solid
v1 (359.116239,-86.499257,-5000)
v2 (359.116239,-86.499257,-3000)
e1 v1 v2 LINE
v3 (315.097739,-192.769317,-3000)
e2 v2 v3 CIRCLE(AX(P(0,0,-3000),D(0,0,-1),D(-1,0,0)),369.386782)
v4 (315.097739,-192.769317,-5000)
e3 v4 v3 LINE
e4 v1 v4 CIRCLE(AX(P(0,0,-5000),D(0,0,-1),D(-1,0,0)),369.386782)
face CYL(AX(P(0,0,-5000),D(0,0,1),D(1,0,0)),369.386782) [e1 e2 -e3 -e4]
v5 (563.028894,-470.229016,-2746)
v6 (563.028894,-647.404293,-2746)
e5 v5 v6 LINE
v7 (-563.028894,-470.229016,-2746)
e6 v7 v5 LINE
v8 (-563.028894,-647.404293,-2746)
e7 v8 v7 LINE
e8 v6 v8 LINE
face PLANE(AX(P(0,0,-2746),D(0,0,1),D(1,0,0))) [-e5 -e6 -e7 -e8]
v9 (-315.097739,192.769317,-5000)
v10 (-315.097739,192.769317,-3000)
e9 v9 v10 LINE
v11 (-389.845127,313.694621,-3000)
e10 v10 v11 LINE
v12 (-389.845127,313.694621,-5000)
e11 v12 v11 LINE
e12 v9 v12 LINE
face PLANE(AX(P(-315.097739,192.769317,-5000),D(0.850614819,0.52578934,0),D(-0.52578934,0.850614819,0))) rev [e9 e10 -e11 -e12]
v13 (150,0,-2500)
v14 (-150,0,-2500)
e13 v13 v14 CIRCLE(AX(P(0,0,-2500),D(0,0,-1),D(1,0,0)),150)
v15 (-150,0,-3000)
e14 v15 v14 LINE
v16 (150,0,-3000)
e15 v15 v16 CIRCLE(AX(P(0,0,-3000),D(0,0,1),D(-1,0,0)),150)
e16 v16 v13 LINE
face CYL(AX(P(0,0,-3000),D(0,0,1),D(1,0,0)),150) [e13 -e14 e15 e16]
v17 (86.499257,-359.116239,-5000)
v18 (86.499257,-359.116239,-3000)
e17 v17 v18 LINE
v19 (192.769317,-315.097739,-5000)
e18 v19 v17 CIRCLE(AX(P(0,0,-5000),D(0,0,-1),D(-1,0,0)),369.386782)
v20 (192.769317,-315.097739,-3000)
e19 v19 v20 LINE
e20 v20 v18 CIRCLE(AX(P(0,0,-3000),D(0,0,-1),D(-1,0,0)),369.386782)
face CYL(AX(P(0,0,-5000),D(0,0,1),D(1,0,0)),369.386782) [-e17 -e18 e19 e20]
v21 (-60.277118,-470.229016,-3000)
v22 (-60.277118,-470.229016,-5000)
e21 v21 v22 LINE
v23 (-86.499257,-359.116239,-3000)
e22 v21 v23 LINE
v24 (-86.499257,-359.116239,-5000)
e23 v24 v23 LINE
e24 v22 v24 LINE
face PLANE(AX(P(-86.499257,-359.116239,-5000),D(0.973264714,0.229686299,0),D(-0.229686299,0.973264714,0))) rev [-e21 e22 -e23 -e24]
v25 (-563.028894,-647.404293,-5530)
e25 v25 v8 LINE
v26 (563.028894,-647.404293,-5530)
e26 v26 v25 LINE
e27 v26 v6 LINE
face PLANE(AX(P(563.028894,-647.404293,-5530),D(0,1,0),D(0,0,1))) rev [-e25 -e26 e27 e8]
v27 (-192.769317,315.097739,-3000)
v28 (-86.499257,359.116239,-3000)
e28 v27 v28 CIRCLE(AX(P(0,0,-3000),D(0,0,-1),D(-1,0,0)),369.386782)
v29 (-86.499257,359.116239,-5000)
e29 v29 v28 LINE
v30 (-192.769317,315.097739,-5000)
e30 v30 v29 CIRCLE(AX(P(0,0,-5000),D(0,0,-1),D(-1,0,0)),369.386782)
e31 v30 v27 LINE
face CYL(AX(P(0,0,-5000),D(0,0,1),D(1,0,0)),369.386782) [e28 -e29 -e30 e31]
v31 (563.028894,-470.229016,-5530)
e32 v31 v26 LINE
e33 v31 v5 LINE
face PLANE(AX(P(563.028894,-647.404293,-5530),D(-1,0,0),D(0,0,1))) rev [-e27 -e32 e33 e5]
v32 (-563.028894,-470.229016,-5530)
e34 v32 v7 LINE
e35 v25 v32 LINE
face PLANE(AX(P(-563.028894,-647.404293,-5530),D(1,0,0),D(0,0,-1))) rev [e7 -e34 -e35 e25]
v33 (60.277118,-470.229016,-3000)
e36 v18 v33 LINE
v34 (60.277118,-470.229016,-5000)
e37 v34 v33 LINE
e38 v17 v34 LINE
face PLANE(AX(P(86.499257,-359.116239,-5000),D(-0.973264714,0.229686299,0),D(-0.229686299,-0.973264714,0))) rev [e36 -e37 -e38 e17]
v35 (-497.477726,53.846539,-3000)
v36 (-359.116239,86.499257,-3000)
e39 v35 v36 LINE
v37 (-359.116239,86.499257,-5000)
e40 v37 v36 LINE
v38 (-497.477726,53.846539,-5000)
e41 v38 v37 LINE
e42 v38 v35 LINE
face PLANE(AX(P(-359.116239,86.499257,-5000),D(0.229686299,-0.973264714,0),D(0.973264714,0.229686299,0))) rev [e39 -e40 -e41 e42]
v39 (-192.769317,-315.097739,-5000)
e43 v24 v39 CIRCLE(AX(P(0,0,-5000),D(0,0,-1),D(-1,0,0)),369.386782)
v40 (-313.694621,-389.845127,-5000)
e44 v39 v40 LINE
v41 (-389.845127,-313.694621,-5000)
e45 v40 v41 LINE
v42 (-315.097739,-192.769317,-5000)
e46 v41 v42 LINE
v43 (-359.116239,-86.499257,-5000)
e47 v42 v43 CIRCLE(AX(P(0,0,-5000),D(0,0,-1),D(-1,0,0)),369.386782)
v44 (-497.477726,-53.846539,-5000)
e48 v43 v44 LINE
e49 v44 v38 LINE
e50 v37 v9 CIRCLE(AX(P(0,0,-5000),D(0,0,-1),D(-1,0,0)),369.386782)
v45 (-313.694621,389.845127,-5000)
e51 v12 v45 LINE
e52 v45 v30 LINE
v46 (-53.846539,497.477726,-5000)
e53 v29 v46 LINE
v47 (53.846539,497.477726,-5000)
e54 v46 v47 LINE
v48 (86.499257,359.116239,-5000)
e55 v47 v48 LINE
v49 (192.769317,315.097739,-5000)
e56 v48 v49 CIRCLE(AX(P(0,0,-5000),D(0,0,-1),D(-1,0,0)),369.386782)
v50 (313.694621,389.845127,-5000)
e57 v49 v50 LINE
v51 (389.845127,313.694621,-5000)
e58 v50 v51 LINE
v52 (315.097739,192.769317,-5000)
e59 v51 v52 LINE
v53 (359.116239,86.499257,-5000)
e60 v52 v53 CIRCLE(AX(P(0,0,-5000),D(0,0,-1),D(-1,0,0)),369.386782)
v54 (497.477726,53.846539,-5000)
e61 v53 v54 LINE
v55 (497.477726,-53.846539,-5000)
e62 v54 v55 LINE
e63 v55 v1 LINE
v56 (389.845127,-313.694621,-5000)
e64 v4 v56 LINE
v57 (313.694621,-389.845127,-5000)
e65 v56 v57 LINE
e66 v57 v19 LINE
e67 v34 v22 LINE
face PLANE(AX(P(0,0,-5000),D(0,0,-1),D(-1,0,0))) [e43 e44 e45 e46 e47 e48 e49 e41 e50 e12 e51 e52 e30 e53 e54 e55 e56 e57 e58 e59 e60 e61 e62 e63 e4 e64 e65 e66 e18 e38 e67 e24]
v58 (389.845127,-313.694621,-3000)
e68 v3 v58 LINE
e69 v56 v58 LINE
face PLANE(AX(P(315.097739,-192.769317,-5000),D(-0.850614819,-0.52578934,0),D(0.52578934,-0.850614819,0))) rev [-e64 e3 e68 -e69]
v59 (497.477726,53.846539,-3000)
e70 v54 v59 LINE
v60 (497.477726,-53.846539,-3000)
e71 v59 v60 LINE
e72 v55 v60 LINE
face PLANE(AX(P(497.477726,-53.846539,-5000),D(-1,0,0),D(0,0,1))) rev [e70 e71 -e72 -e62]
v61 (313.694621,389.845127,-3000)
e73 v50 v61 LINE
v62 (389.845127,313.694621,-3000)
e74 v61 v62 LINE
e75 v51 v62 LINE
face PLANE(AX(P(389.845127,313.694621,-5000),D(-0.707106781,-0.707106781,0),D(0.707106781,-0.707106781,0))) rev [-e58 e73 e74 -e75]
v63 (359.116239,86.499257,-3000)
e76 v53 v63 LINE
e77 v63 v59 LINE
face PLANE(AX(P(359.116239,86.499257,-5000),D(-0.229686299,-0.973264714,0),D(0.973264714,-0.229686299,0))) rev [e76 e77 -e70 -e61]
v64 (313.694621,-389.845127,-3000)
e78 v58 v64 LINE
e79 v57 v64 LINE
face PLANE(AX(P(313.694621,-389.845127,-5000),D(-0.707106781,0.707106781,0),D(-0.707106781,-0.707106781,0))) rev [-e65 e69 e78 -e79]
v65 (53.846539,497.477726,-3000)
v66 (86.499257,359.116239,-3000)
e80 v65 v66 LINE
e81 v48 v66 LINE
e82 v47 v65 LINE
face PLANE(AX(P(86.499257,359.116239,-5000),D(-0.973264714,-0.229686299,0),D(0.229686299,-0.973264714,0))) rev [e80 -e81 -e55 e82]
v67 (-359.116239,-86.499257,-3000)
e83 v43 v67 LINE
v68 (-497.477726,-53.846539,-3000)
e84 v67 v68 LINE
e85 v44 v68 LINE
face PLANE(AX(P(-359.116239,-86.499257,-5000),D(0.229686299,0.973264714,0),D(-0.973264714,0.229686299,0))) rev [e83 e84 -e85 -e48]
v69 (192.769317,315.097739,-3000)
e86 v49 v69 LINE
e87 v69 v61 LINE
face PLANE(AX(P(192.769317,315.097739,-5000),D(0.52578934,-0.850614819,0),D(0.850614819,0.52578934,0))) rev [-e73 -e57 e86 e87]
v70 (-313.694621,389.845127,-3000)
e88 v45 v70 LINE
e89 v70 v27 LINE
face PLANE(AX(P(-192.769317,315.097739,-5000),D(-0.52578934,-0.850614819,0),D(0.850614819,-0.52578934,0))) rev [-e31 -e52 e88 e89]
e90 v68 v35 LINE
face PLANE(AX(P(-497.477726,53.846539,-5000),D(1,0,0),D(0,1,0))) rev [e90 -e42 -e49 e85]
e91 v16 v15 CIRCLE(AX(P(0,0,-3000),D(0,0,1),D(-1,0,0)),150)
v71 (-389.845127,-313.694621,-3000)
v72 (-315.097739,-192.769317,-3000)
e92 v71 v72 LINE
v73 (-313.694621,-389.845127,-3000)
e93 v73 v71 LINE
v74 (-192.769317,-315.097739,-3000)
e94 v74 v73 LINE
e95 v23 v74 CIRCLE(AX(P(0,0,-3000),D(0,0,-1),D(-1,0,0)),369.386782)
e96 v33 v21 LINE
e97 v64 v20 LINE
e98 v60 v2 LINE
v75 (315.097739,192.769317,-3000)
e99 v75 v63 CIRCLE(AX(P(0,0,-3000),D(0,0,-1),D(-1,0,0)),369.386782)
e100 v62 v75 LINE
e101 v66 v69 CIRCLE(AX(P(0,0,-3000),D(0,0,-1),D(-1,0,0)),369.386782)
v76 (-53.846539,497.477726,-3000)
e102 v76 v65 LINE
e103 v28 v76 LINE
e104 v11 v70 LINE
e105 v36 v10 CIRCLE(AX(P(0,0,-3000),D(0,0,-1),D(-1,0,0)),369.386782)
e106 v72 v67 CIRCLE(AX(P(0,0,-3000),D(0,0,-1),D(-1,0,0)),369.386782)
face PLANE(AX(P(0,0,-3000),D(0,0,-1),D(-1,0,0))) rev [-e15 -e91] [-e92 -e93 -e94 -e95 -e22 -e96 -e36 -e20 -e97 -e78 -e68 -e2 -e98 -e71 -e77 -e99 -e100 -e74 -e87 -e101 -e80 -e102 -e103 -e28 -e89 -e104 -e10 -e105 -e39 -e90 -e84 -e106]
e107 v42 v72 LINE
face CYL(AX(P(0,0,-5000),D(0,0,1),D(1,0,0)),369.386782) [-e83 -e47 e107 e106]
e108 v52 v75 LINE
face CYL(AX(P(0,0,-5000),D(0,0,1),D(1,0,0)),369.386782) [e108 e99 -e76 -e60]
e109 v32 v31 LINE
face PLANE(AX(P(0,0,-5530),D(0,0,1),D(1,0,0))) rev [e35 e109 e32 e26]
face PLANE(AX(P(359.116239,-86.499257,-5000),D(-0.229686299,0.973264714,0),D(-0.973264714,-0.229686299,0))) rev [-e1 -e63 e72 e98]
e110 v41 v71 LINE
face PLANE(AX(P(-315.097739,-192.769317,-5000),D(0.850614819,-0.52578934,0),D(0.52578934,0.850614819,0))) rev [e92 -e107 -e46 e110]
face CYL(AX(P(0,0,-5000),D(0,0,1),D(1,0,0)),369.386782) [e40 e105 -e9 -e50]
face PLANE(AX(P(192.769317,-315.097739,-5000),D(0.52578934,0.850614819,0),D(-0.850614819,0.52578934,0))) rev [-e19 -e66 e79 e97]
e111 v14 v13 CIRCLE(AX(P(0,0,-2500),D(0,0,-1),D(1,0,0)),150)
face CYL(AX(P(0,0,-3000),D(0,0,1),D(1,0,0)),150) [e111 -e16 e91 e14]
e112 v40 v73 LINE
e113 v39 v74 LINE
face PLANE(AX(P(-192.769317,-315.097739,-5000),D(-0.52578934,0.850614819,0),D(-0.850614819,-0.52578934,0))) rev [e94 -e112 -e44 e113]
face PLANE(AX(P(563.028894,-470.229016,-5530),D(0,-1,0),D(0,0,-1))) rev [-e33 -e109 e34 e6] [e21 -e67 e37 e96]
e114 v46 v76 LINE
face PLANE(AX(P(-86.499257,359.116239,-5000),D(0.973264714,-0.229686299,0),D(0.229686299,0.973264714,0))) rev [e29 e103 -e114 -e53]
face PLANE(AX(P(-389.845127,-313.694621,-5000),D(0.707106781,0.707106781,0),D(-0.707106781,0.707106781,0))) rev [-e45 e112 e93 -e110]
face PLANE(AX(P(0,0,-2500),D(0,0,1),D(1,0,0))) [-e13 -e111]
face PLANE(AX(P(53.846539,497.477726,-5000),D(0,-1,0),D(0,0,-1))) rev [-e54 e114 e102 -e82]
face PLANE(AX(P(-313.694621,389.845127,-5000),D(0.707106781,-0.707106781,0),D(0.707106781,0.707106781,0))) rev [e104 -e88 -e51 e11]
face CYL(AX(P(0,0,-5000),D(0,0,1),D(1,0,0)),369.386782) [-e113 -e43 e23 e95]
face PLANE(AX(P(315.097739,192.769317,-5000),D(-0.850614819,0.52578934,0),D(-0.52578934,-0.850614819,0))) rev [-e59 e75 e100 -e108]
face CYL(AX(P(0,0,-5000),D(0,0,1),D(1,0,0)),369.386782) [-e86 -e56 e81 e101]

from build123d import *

# Parameters (mm, degrees)
SKETCH1_R                = 150
BOSS_EXTRUDE1_DEPTH      = 3000
CUT_EXTRUDE1_DEPTH       = 435
BOSS_EXTRUDE3_DEPTH      = 2000
BOSS_EXTRUDE4_DEPTH      = 530
BOSS_EXTRUDE4_DEPTH_BACK = 2254
SKETCH5_W                = 1126.0577882
SKETCH5_H                = 177.175277377
BOSS_EXTRUDE5_DEPTH      = 75
SKETCH8_R                = 377.253593713
CUT_EXTRUDE2_DEPTH       = 2500


with BuildPart() as part:
    # Sketch1 → Boss-Extrude1 (new body)
    with BuildSketch(Plane.XY):
        Circle(SKETCH1_R)
    extrude(amount=-BOSS_EXTRUDE1_DEPTH)

    # Sketch2 → Cut-Extrude1 (cut)
    with BuildSketch(Plane(origin=(0, 0, 0), x_dir=(1, 0, 0), z_dir=(0, 1, 0))):
        with BuildLine():
            Line((-50, 150), (-50, 450))
            ThreePointArc((-50, 450), (0, 500), (50, 450))
            Line((50, 450), (50, 150))
            ThreePointArc((50, 150), (0, 100), (-50, 150))
        make_face()
    extrude(amount=CUT_EXTRUDE1_DEPTH, mode=Mode.SUBTRACT)

    # Sketch4 → Boss-Extrude3 (add)
    with BuildSketch(Plane(origin=(0, 0, -3000), x_dir=(-1, 0, 0), z_dir=(0, 0, -1))):
        with BuildLine():
            Line((-86.499256684, 359.11623894), (-53.846539015, 497.477726118))
            Line((-53.846539015, 497.477726118), (53.846539015, 497.477726118))
            Line((53.846539015, 497.477726118), (86.499256684, 359.11623894))
            ThreePointArc((86.499256684, 359.11623894), (141.358201482, 341.268887171), (192.76931682, 315.097738757))
            Line((192.76931682, 315.097738757), (313.694620747, 389.845126508))
            Line((313.694620747, 389.845126508), (389.845126508, 313.694620747))
            Line((389.845126508, 313.694620747), (315.097738757, 192.76931682))
            ThreePointArc((315.097738757, 192.76931682), (341.268887171, 141.358201482), (359.11623894, 86.499256684))
            Line((359.11623894, 86.499256684), (497.477726118, 53.846539015))
            Line((497.477726118, 53.846539015), (497.477726118, -53.846539015))
            Line((497.477726118, -53.846539015), (359.11623894, -86.499256684))
            ThreePointArc((359.11623894, -86.499256684), (341.268887171, -141.358201482), (315.097738757, -192.76931682))
            Line((315.097738757, -192.76931682), (389.845126508, -313.694620747))
            Line((389.845126508, -313.694620747), (313.694620747, -389.845126508))
            Line((313.694620747, -389.845126508), (192.76931682, -315.097738757))
            ThreePointArc((192.76931682, -315.097738757), (141.358201482, -341.268887171), (86.499256684, -359.11623894))
            Line((86.499256684, -359.11623894), (53.846539015, -497.477726118))
            Line((53.846539015, -497.477726118), (-53.846539015, -497.477726118))
            Line((-53.846539015, -497.477726118), (-86.499256684, -359.11623894))
            ThreePointArc((-86.499256684, -359.11623894), (-141.358201482, -341.268887171), (-192.76931682, -315.097738757))
            Line((-192.76931682, -315.097738757), (-313.694620747, -389.845126508))
            Line((-313.694620747, -389.845126508), (-389.845126508, -313.694620747))
            Line((-389.845126508, -313.694620747), (-315.097738757, -192.76931682))
            ThreePointArc((-315.097738757, -192.76931682), (-341.268887171, -141.358201482), (-359.11623894, -86.499256684))
            Line((-359.11623894, -86.499256684), (-497.477726118, -53.846539015))
            Line((-497.477726118, -53.846539015), (-497.477726118, 53.846539015))
            Line((-497.477726118, 53.846539015), (-359.11623894, 86.499256684))
            ThreePointArc((-359.11623894, 86.499256684), (-341.268887171, 141.358201482), (-315.097738757, 192.76931682))
            Line((-315.097738757, 192.76931682), (-389.845126508, 313.694620747))
            Line((-389.845126508, 313.694620747), (-313.694620747, 389.845126508))
            Line((-313.694620747, 389.845126508), (-192.76931682, 315.097738757))
            ThreePointArc((-192.76931682, 315.097738757), (-141.358201482, 341.268887171), (-86.499256684, 359.11623894))
        make_face()
    extrude(amount=BOSS_EXTRUDE3_DEPTH)

    # Sketch5 → Boss-Extrude4 (add, two sides: drawn at the far end of the back side and taken through both)
    with BuildSketch(Plane(origin=(0, 0, -5000), x_dir=(-1, 0, 0), z_dir=(0, 0, -1)).offset(-BOSS_EXTRUDE4_DEPTH_BACK)):
        with Locations((0, -558.816654709)):
            Rectangle(SKETCH5_W, SKETCH5_H)
    extrude(amount=BOSS_EXTRUDE4_DEPTH + BOSS_EXTRUDE4_DEPTH_BACK)

    # Sketch6 → Boss-Extrude5 (add)
    with BuildSketch(Plane(origin=(0, 0, 0), x_dir=(1, 0, 0), z_dir=(0, 1, 0))):
        with BuildLine():
            Line((50, 150), (50, 450))
            ThreePointArc((50, 450), (0, 500), (-50, 450))
            Line((-50, 450), (-50, 150))
            ThreePointArc((-50, 150), (0, 100), (50, 150))
        make_face()
    extrude(amount=BOSS_EXTRUDE5_DEPTH)

    # Sketch8 → Cut-Extrude2 (cut)
    with BuildSketch(Plane.XY):
        Circle(SKETCH8_R)
    extrude(amount=-CUT_EXTRUDE2_DEPTH, mode=Mode.SUBTRACT)


solid = part.part
